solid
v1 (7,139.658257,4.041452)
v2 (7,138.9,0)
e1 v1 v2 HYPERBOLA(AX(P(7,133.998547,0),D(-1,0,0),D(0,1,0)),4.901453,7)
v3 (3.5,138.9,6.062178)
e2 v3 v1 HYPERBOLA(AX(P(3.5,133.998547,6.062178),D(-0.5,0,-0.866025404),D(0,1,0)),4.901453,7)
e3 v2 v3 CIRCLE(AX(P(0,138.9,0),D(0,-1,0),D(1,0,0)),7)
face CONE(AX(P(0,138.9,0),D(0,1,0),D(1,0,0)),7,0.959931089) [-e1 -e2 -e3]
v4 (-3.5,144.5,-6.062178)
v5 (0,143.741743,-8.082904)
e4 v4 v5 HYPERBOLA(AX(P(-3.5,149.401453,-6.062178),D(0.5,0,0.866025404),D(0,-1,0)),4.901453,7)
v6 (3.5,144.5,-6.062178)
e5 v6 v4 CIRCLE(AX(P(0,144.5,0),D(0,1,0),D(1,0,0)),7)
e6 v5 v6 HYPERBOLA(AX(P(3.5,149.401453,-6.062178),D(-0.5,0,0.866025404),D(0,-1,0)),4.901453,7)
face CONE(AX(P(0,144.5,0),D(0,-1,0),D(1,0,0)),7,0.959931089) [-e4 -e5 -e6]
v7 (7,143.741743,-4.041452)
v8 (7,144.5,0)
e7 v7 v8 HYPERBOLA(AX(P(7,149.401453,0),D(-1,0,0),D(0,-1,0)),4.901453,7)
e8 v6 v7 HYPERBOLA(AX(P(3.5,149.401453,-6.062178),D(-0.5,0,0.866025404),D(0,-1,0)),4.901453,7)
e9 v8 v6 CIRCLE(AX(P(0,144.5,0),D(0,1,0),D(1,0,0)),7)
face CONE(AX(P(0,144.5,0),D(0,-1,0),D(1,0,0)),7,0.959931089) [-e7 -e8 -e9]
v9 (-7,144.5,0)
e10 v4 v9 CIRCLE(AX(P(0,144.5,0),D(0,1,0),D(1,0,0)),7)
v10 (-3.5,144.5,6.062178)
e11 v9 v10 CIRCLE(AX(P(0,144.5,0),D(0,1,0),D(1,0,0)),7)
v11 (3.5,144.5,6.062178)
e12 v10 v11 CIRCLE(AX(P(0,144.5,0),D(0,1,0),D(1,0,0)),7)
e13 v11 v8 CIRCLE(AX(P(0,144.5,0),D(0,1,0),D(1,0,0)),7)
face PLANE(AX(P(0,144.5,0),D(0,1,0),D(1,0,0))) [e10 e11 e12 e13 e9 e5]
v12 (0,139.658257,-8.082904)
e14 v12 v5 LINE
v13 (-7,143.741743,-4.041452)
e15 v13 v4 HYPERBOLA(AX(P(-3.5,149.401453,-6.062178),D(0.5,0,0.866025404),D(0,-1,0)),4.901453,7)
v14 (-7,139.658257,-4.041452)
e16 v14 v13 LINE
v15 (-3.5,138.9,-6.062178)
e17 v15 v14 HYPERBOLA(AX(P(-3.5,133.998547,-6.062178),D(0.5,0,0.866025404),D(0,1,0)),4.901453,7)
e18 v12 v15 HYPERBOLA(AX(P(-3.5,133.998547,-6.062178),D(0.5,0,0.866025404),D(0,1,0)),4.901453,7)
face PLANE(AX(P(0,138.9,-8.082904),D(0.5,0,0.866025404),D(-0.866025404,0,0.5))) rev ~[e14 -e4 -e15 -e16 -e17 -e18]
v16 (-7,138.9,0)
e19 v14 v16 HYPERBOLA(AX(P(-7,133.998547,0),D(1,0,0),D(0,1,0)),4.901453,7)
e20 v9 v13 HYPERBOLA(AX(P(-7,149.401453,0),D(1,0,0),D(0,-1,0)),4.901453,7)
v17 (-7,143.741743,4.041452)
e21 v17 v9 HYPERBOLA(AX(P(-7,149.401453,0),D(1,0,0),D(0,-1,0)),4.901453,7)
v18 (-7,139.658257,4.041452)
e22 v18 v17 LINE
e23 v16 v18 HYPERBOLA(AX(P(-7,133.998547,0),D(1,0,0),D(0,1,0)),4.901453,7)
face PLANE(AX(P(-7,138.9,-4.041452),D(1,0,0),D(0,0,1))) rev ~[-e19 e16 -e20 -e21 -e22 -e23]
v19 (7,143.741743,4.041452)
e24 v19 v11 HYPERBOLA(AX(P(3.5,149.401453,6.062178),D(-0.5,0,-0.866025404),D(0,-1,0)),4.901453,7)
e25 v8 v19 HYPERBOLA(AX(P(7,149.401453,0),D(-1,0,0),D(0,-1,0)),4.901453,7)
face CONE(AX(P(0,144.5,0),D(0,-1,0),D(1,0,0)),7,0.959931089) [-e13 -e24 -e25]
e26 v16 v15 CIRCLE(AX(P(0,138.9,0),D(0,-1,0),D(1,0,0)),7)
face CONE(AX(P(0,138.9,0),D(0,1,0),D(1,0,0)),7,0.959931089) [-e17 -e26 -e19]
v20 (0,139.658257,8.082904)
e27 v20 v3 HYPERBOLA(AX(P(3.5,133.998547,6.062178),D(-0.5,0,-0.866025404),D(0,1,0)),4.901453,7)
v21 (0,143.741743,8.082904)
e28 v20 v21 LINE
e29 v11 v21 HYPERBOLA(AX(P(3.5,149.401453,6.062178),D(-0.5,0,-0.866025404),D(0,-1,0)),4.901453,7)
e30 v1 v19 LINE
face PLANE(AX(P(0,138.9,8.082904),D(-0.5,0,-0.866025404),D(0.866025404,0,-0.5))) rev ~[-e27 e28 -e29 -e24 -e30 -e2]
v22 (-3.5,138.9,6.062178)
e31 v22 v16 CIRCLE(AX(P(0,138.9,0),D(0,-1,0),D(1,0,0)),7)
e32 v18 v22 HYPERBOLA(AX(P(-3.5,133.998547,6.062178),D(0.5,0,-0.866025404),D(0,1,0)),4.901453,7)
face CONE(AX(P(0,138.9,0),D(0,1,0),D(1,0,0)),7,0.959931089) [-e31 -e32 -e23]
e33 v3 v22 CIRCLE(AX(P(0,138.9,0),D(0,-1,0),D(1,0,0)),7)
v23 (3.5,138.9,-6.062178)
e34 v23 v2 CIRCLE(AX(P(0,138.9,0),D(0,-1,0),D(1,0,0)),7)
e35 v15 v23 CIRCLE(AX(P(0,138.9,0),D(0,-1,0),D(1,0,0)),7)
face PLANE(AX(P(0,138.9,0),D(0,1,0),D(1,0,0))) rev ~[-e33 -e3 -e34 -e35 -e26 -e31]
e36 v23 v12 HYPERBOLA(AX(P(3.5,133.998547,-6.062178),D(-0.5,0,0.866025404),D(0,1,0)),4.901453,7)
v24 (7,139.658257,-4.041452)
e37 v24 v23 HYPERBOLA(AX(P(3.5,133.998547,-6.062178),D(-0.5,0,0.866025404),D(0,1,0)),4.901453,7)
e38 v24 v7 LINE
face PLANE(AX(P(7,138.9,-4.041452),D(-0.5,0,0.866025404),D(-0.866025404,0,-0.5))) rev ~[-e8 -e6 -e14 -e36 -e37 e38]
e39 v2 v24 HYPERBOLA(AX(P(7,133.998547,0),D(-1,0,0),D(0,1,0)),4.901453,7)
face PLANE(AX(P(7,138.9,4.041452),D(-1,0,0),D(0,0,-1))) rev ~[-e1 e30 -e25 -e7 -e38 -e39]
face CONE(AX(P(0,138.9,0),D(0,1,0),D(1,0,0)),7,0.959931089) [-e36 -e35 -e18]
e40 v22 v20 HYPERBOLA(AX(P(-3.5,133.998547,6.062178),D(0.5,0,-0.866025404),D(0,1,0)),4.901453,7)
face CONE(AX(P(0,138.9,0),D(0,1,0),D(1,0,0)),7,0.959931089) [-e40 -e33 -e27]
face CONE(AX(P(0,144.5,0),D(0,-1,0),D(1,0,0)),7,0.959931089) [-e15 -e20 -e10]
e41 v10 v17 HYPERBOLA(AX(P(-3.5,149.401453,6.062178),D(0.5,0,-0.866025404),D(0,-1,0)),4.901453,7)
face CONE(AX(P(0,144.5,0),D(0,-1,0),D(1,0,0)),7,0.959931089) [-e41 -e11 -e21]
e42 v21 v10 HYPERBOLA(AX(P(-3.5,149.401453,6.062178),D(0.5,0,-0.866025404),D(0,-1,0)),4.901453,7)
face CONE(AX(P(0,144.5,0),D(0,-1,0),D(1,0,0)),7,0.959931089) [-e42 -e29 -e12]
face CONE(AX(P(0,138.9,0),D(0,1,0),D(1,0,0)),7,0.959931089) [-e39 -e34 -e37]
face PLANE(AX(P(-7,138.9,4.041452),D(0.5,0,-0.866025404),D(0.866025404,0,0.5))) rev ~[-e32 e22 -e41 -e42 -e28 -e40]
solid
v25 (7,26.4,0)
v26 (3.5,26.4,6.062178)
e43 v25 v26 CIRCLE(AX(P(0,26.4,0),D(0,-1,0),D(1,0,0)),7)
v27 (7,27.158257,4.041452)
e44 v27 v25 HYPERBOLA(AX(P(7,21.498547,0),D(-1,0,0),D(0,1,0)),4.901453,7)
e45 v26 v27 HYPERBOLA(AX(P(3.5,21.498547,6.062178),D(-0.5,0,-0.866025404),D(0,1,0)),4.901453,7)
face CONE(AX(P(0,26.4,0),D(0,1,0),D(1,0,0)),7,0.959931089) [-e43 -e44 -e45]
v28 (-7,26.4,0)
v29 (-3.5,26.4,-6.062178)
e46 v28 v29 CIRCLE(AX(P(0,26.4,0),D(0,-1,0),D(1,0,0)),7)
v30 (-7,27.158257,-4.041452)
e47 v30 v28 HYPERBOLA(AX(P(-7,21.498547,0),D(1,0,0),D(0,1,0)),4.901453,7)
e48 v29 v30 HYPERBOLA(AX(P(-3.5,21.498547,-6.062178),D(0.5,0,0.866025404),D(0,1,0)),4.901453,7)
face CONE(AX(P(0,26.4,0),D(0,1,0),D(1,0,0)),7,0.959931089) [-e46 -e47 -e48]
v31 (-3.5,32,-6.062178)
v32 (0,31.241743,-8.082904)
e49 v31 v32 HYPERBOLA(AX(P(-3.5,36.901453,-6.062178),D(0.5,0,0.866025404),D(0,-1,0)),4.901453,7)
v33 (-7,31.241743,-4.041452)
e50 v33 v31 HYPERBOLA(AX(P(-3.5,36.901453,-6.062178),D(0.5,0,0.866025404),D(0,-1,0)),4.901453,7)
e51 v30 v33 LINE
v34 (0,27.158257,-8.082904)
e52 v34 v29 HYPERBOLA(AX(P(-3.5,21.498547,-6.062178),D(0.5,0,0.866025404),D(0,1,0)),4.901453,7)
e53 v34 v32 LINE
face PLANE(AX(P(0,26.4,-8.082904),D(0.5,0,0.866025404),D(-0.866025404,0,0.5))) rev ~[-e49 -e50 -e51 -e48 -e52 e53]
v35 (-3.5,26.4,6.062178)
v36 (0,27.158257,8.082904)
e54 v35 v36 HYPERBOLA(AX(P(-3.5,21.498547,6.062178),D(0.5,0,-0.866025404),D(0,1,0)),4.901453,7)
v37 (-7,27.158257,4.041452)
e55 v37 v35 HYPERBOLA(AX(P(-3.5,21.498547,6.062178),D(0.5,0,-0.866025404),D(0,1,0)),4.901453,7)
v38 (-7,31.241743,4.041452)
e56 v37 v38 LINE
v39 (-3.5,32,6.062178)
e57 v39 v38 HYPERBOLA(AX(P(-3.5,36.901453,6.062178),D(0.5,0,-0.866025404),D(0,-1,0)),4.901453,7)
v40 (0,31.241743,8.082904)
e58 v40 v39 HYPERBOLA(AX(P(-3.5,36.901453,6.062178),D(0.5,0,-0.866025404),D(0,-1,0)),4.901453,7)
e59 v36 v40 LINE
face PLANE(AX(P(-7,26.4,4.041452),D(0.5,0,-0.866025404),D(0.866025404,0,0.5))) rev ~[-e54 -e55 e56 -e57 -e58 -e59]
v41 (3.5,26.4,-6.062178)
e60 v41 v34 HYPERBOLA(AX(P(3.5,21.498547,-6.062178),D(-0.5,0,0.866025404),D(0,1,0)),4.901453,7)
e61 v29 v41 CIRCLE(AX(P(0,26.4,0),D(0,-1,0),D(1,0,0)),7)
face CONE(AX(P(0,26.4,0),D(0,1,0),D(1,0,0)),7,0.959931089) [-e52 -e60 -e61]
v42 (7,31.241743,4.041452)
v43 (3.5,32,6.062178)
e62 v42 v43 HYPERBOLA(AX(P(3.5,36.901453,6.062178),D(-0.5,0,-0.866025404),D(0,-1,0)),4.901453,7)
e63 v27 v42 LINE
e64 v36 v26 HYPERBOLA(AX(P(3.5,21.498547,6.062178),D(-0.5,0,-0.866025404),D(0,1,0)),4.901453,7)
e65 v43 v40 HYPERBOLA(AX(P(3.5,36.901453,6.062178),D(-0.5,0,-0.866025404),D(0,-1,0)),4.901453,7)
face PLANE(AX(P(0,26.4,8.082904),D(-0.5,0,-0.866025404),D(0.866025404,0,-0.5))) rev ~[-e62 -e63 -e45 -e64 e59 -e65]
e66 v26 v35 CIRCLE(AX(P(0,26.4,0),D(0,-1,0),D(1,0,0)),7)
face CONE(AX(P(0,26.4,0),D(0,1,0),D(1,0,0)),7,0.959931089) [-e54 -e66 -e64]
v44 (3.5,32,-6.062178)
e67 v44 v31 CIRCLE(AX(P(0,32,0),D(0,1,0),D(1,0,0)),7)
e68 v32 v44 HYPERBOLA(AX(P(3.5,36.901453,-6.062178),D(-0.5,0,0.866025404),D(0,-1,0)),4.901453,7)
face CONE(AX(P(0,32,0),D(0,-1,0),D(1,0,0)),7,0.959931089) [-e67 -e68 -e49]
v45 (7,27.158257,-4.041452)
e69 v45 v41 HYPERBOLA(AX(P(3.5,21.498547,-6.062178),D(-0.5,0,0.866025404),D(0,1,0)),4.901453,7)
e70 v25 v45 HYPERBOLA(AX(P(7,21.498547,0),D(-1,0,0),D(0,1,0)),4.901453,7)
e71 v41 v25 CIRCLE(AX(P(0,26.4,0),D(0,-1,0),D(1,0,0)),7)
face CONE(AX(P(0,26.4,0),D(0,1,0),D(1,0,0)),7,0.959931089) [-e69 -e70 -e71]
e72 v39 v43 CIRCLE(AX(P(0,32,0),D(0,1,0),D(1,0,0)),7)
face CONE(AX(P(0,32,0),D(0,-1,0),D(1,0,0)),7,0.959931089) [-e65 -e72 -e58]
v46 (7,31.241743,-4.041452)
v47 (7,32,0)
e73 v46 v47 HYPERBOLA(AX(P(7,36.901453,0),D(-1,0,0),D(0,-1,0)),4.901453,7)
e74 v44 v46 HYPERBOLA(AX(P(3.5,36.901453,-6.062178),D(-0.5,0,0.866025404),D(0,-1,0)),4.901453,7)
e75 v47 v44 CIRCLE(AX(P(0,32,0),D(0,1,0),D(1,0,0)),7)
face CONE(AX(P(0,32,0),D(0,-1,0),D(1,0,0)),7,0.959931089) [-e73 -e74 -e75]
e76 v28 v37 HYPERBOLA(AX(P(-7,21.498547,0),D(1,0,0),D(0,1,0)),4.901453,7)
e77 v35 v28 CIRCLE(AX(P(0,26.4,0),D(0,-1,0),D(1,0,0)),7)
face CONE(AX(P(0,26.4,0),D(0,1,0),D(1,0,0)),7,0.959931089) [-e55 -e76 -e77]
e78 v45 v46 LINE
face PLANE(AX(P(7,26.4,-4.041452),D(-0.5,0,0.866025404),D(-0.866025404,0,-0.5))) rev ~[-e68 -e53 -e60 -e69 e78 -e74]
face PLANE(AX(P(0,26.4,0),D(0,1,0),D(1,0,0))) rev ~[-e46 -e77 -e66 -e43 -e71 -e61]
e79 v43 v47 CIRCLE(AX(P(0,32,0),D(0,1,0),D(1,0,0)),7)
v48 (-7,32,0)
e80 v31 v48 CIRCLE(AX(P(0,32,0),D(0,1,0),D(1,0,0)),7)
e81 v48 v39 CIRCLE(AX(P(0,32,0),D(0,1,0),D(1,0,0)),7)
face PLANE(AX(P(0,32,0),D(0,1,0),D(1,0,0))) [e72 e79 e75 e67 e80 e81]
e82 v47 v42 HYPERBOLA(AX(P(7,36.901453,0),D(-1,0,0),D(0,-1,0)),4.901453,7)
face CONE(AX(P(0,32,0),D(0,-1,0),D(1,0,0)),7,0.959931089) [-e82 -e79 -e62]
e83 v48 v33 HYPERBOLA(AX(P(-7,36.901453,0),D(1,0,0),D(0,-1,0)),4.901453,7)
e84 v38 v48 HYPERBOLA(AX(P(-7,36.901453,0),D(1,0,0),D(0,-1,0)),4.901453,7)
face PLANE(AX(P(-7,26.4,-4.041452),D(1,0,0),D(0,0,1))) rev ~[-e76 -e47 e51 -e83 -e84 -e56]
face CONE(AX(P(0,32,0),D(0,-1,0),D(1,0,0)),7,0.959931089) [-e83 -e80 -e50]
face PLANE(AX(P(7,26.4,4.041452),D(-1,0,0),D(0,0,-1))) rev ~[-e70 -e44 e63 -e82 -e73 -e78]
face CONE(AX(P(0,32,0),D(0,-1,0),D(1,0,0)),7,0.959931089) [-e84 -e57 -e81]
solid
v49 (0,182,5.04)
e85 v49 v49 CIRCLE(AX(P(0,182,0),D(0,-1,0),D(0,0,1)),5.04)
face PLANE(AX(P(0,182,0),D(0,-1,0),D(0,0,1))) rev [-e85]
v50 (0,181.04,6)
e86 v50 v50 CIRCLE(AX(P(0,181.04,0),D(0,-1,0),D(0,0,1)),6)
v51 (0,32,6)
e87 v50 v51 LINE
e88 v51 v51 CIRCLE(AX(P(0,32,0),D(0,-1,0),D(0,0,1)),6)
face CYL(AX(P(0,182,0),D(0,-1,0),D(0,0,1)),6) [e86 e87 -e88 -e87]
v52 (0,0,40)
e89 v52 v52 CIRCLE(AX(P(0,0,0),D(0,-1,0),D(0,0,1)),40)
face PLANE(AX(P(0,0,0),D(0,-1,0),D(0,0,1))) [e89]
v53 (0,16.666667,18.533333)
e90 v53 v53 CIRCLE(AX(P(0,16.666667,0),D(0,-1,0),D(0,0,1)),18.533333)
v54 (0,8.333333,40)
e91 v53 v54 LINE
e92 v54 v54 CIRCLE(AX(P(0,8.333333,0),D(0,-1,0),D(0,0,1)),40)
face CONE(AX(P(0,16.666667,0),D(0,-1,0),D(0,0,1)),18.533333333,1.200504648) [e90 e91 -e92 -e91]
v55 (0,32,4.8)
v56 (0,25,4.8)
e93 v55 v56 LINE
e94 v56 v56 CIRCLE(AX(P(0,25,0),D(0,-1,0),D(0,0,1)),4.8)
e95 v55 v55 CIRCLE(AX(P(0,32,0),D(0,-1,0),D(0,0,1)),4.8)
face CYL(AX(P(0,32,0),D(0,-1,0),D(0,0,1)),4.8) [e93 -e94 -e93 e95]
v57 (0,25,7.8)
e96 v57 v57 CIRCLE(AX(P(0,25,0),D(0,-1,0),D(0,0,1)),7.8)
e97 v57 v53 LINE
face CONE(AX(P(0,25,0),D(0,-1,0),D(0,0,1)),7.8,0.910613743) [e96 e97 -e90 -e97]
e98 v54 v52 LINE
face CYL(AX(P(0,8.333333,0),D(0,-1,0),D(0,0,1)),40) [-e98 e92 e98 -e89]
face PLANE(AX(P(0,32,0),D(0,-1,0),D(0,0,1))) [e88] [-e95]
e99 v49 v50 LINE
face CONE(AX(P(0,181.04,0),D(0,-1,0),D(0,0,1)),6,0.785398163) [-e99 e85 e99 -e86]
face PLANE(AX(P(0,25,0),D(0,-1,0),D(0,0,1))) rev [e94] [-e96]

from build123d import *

# Parameters (mm, degrees)
CHAMFER1_SIZE       = 0.96
BOSS_EXTRUDE1_START = 26.4
BOSS_EXTRUDE1_DEPTH = 5.6
BOSS_EXTRUDE2_START = 138.9
BOSS_EXTRUDE2_DEPTH = 5.6
SKETCH6_R           = 9.165807537
SKETCH6_R_2         = 7
CUT_EXTRUDE4_DEPTH  = 5.6
CUT_EXTRUDE4_TAPER  = 55
SKETCH7_R           = 9.165807537
SKETCH7_R_2         = 7
CUT_EXTRUDE5_DEPTH  = 5.6
CUT_EXTRUDE5_TAPER  = 55
SKETCH9_R           = 9.165807537
SKETCH9_R_2         = 7
CUT_EXTRUDE6_DEPTH  = 5.6
CUT_EXTRUDE6_TAPER  = 55
SKETCH10_R          = 9.165807537
SKETCH10_R_2        = 7
CUT_EXTRUDE7_DEPTH  = 5.6
CUT_EXTRUDE7_TAPER  = 55


with BuildPart() as part:
    # Sketch2 → Revolve1 (revolve)
    with BuildSketch(Plane(origin=(0, 0, 0), x_dir=(0, 0, -1), z_dir=(1, 0, 0)), mode=Mode.PRIVATE) as revolve1_sk:
        Polygon((4.8, 32), (4.8, 25), (7.8, 25), (18.533333333, 16.666666667), (40, 8.333333333), (40, 0), (0, 0), (0, 182), (6, 182), (6, 32), align=None)
    revolve(revolve1_sk.sketch.rotate(Axis((0, 182, 0), (0, -1, 0)), 180), axis=Axis((0, 182, 0), (0, -1, 0)))

    # Chamfer1
    chamfer1_edges = [part.edges().sort_by_distance(p)[0] for p in [
        (0, 182, -6),
    ]]
    chamfer(chamfer1_edges, length=CHAMFER1_SIZE)


with BuildPart() as body_2:
    # Sketch3 → Boss-Extrude1 (new body)
    with BuildSketch(Plane(origin=(0, 0, 0), x_dir=(1, 0, 0), z_dir=(0, 1, 0)).offset(BOSS_EXTRUDE1_START)):
        Polygon((7, -4.041451884), (7, 4.041451884), (0, 8.082903769), (-7, 4.041451884), (-7, -4.041451884), (0, -8.082903769), align=None)
    extrude(amount=BOSS_EXTRUDE1_DEPTH)

    # Sketch6 → Cut-Extrude4 (cut)
    with BuildSketch(Plane(origin=(0, 32, 0), x_dir=(1, 0, 0), z_dir=(0, 1, 0))):
        Circle(SKETCH6_R)
        Circle(SKETCH6_R_2, mode=Mode.SUBTRACT)
    extrude(amount=-CUT_EXTRUDE4_DEPTH, taper=CUT_EXTRUDE4_TAPER, mode=Mode.SUBTRACT)

    # Sketch7 → Cut-Extrude5 (cut)
    with BuildSketch(Plane.XZ.offset(-26.4)):
        Circle(SKETCH7_R)
        Circle(SKETCH7_R_2, mode=Mode.SUBTRACT)
    extrude(amount=-CUT_EXTRUDE5_DEPTH, taper=CUT_EXTRUDE5_TAPER, mode=Mode.SUBTRACT)


with BuildPart() as body_3:
    # Sketch8 → Boss-Extrude2 (new body)
    with BuildSketch(Plane(origin=(0, 0, 0), x_dir=(1, 0, 0), z_dir=(0, 1, 0)).offset(BOSS_EXTRUDE2_START)):
        Polygon((7, -4.041451884), (7, 4.041451884), (0, 8.082903769), (-7, 4.041451884), (-7, -4.041451884), (0, -8.082903769), align=None)
    extrude(amount=BOSS_EXTRUDE2_DEPTH)

    # Sketch9 → Cut-Extrude6 (cut)
    with BuildSketch(Plane(origin=(0, 144.5, 0), x_dir=(1, 0, 0), z_dir=(0, 1, 0))):
        Circle(SKETCH9_R)
        Circle(SKETCH9_R_2, mode=Mode.SUBTRACT)
    extrude(amount=-CUT_EXTRUDE6_DEPTH, taper=CUT_EXTRUDE6_TAPER, mode=Mode.SUBTRACT)

    # Sketch10 → Cut-Extrude7 (cut)
    with BuildSketch(Plane.XZ.offset(-138.9)):
        Circle(SKETCH10_R)
        Circle(SKETCH10_R_2, mode=Mode.SUBTRACT)
    extrude(amount=-CUT_EXTRUDE7_DEPTH, taper=CUT_EXTRUDE7_TAPER, mode=Mode.SUBTRACT)


solid = Compound([part.part, body_2.part, body_3.part])
